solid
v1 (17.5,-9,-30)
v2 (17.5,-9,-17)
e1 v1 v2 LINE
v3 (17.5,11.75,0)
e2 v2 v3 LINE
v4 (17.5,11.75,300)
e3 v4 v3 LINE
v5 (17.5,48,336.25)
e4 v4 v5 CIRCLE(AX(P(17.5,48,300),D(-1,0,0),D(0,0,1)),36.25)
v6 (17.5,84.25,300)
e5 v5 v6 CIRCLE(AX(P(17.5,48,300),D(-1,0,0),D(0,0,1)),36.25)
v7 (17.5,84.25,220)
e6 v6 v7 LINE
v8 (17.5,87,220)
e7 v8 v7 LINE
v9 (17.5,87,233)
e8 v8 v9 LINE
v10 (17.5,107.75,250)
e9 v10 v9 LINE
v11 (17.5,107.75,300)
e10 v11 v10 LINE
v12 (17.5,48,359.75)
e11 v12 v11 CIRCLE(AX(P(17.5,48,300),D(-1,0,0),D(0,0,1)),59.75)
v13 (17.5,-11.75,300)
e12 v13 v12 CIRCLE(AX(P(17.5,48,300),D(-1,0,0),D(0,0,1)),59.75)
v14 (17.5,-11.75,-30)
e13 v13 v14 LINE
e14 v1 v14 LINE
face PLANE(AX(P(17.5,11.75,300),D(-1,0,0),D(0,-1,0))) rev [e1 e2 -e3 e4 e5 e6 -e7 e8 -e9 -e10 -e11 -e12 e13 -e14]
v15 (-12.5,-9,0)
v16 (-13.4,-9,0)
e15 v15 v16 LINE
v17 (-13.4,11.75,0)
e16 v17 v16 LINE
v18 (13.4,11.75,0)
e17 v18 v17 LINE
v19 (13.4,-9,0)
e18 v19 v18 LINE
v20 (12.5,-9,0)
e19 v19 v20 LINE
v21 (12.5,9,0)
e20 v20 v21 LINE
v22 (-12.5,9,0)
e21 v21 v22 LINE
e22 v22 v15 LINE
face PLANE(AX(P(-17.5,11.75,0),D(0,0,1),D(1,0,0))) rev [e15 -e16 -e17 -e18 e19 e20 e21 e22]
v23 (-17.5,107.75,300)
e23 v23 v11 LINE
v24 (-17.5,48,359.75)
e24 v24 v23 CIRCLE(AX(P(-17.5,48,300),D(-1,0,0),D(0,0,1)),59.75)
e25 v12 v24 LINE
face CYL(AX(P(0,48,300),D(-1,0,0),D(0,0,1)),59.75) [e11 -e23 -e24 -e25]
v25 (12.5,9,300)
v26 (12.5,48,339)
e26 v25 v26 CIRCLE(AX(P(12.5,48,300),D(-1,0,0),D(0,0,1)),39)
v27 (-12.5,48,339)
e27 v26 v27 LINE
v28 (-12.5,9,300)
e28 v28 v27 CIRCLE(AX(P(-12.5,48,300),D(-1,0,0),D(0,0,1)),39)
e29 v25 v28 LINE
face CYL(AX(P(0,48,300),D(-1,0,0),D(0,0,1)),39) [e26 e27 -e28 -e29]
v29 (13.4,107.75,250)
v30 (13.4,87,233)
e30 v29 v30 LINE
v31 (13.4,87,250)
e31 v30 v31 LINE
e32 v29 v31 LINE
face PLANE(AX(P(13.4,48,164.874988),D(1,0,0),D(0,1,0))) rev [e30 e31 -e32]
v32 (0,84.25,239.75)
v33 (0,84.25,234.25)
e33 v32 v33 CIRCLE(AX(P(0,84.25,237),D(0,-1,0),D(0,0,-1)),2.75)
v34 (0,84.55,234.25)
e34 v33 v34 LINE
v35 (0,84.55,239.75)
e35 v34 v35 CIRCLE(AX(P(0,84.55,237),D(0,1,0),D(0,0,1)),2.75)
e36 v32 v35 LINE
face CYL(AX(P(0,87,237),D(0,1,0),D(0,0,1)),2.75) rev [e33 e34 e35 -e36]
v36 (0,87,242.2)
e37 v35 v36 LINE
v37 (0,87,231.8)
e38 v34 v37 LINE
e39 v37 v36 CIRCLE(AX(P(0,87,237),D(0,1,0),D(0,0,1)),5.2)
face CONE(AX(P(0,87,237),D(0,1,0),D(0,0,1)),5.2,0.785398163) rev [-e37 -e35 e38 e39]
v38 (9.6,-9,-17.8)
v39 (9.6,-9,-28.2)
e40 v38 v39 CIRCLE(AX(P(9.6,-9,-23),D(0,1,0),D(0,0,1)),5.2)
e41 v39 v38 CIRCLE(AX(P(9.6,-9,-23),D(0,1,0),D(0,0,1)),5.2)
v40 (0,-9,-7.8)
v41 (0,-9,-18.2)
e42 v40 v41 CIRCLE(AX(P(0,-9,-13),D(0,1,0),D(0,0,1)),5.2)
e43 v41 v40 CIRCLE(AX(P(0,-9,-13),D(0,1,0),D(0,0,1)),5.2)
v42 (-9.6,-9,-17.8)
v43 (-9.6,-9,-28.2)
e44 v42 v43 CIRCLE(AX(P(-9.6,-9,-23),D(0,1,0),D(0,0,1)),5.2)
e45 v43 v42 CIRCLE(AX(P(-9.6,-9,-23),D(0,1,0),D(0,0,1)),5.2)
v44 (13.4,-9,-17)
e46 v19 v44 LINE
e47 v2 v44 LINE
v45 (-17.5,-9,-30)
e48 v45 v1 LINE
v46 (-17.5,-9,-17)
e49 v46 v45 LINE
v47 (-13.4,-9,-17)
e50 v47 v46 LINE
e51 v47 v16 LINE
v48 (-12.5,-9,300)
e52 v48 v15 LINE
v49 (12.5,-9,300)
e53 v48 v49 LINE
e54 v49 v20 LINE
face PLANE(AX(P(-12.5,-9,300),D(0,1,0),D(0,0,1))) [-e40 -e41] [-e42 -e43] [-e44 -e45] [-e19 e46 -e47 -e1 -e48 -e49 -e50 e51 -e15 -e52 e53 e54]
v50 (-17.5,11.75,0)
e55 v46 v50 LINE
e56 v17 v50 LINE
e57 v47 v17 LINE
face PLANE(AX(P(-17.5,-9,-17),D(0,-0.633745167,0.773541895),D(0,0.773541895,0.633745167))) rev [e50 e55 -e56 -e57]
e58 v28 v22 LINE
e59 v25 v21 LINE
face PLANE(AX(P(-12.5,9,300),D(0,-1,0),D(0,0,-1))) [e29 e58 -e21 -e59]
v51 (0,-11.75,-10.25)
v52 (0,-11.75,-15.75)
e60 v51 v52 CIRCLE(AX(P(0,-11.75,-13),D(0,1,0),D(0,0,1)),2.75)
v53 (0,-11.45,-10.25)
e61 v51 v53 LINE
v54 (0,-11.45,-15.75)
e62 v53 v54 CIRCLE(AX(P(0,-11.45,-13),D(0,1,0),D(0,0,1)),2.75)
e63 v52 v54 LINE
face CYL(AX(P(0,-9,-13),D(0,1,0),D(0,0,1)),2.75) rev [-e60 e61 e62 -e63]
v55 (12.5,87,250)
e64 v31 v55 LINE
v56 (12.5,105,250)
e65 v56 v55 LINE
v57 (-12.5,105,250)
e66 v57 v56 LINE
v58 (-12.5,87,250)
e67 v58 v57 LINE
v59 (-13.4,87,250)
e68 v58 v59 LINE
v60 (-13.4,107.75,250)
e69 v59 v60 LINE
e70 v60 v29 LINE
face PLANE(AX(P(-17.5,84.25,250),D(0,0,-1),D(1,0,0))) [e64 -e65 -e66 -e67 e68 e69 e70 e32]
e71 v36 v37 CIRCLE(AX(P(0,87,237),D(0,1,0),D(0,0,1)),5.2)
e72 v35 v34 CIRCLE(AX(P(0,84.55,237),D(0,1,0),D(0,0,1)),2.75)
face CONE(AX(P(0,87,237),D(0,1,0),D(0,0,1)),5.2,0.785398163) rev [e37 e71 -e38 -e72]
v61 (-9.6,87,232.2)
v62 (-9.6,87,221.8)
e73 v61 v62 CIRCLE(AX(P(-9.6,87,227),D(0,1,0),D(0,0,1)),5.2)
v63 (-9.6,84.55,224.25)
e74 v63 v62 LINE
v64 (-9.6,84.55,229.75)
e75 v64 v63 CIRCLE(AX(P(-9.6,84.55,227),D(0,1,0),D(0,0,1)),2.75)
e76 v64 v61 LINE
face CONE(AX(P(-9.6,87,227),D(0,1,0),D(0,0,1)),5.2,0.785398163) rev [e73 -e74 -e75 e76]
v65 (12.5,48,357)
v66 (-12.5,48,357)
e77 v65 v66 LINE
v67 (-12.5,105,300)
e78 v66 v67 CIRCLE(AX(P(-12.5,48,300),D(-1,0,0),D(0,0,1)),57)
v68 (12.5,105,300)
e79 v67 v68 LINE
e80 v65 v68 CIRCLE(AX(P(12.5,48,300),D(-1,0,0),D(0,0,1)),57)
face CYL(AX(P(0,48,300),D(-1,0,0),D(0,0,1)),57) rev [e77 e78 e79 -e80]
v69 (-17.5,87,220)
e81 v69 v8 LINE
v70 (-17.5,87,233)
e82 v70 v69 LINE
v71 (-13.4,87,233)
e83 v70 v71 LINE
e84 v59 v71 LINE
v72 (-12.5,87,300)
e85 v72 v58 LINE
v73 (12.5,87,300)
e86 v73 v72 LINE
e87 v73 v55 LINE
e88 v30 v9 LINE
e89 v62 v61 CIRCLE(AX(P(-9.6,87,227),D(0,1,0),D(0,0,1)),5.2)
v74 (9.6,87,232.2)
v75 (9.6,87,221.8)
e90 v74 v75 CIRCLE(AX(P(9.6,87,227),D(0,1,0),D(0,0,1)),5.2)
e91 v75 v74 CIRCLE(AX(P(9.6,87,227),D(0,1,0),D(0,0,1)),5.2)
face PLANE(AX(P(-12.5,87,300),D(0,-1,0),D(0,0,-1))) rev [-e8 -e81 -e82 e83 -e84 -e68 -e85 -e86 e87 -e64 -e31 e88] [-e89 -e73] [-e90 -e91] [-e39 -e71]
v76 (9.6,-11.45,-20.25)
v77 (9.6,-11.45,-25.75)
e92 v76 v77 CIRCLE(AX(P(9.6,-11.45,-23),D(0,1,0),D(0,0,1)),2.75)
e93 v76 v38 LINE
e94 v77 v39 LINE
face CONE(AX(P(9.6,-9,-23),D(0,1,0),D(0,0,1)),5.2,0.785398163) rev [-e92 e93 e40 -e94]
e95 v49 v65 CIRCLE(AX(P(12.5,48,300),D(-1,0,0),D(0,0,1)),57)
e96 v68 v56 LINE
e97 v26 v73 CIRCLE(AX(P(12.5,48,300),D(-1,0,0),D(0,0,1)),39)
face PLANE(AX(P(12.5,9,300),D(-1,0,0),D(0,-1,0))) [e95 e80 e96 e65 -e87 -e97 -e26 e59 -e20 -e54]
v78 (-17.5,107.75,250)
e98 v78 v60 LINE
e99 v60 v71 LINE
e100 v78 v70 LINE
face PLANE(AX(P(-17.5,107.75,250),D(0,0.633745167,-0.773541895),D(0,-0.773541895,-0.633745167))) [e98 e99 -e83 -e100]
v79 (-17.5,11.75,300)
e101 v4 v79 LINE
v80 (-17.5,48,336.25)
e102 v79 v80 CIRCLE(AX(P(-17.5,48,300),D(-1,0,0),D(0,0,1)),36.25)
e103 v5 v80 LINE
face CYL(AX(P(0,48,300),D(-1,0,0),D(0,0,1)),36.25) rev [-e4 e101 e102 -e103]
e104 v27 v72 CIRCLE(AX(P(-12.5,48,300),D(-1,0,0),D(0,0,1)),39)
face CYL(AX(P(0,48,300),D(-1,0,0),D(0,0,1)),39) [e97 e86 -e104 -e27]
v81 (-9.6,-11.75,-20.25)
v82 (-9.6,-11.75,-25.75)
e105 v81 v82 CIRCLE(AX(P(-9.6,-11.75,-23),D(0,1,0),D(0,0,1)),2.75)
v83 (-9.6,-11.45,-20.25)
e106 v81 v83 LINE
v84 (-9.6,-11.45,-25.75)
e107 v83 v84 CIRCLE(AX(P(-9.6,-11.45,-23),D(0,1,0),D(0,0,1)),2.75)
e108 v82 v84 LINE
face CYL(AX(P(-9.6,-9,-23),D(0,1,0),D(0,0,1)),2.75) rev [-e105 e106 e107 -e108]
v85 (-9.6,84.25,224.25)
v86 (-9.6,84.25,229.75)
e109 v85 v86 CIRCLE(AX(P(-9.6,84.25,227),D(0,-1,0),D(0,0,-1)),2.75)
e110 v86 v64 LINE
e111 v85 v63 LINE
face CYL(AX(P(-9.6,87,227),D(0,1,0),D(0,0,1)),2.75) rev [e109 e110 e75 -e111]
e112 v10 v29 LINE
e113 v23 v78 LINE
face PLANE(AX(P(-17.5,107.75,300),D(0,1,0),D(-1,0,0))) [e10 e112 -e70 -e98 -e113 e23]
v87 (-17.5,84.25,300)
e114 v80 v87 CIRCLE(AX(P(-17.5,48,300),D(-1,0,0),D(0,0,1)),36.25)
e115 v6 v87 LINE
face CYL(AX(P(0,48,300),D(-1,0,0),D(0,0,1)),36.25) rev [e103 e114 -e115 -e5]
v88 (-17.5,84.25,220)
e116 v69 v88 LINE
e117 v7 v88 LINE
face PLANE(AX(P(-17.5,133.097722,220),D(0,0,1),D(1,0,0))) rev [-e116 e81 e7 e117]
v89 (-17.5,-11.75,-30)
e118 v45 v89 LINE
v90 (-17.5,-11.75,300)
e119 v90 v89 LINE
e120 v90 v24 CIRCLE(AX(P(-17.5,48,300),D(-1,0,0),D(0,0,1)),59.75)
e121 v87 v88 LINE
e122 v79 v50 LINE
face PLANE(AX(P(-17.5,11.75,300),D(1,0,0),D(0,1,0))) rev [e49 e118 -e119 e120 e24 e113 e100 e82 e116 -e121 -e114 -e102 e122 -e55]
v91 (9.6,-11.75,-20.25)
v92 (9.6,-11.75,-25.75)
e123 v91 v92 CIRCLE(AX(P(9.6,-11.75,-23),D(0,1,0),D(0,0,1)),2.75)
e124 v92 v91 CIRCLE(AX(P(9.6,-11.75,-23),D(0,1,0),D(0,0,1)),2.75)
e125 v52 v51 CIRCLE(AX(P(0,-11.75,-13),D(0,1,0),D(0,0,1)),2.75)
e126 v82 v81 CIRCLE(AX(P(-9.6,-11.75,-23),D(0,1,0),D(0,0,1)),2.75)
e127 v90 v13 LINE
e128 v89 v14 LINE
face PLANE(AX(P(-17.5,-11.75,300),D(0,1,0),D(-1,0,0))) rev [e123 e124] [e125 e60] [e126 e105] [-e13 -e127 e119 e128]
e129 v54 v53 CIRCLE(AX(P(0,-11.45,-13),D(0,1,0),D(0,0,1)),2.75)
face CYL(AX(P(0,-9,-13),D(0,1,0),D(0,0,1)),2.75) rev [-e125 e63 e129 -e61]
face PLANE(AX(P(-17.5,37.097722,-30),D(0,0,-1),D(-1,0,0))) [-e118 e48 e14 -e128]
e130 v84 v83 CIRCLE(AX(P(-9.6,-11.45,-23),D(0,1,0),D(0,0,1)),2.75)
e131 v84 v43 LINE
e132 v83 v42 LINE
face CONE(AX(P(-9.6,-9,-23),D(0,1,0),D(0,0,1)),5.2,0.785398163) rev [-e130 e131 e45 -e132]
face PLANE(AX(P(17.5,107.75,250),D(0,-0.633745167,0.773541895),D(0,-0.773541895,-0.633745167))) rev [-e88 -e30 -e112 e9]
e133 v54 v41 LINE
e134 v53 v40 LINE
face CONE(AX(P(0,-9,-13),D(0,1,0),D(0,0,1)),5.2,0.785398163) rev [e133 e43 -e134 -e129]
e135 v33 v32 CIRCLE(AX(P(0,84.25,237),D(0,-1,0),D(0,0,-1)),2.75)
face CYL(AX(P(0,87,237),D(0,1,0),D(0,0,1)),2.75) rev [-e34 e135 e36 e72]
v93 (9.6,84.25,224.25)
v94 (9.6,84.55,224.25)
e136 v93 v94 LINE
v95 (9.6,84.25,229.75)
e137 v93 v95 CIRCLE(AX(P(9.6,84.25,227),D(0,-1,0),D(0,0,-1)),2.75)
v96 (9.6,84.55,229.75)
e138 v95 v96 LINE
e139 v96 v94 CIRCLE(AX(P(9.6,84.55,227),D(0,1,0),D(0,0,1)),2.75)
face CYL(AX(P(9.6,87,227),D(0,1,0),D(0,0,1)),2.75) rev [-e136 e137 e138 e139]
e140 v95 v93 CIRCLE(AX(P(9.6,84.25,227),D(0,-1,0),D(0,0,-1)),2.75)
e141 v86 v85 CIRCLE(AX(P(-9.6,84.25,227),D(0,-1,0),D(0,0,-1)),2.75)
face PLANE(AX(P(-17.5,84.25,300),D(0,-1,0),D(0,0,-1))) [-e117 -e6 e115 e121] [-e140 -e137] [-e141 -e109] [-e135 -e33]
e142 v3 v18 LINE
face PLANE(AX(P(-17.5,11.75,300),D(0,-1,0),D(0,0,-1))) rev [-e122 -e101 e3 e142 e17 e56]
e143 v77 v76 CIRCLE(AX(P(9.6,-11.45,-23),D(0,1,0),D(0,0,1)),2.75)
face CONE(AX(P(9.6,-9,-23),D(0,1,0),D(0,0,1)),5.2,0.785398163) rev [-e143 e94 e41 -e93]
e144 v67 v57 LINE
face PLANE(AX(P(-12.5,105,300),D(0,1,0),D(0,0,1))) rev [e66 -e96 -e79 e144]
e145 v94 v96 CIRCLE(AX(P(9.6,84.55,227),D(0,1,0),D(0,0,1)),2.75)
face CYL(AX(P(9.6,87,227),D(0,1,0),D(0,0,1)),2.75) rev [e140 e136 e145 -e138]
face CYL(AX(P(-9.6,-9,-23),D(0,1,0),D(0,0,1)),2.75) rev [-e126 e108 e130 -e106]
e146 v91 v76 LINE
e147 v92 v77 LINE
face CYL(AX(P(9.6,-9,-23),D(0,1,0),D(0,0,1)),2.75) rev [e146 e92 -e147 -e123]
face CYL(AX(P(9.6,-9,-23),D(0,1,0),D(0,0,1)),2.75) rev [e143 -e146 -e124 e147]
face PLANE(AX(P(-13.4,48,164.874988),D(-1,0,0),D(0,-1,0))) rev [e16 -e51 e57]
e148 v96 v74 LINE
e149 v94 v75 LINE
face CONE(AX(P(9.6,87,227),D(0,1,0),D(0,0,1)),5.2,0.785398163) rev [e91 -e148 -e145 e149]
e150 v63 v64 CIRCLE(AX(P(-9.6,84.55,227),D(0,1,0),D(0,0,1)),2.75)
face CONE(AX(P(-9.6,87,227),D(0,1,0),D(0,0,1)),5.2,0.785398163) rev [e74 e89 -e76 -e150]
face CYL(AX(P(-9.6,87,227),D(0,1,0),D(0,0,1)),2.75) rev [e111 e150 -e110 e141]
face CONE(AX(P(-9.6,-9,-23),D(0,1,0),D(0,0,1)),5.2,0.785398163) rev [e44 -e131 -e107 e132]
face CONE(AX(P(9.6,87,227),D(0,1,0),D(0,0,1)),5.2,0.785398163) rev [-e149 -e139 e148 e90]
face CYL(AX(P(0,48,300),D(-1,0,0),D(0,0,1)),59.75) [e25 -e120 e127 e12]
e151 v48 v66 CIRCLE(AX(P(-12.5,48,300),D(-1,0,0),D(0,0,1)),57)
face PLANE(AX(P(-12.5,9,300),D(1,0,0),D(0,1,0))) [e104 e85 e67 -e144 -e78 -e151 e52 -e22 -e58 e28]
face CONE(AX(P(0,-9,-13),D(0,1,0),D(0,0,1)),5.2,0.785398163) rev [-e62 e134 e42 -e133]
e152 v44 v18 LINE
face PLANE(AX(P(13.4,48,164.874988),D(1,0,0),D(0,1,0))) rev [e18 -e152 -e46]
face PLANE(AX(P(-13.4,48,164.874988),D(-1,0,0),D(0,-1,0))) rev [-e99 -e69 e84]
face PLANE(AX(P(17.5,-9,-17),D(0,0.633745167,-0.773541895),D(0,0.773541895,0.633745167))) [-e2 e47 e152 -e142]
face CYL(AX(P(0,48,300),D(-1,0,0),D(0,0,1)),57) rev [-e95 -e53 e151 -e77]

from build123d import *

# Parameters (mm, degrees)
SECTION_SIZE_W                              = 35
SECTION_SIZE_H                              = 23.5
SECTION_SIZE_W_2                            = 25
SECTION_SIZE_H_2                            = 18
SKETCH2_W                                   = 35
SKETCH2_H                                   = 30
FITTING114_4_12PZ_1_DEPTH                   = 2.75
SKETCH6_W                                   = 35
SKETCH6_H                                   = 30
FITTING114_4_12PZ_2_DEPTH                   = 2.75
RIB_E_REACH                                 = 379.167
SKETCH9_WALL_W                              = 783.159137046
SKETCH9_WALL_H                              = 4.1
RIB_Z_REACH                                 = 379.167
SKETCH10_WALL_W                             = 783.159137046
SKETCH10_WALL_H                             = 4.1
M5_FLAT_HEAD_SCREW_COUNTERSINK1_AT_2_COUNT  = 2
M5_FLAT_HEAD_SCREW_COUNTERSINK1_AT_2_PITCH  = 13.862178761
M5_FLAT_HEAD_SCREW_COUNTERSINK1_AT_3_COUNT  = 2
M5_FLAT_HEAD_SCREW_COUNTERSINK1_AT_3_PITCH  = 19.2
M5_FLAT_HEAD_SCREW_COUNTERSINK2_D           = 5.5
M5_FLAT_HEAD_SCREW_COUNTERSINK2_DEPTH       = 35
M5_FLAT_HEAD_SCREW_COUNTERSINK2_CSINK_D     = 10.4
M5_FLAT_HEAD_SCREW_COUNTERSINK2_CSINK_ANGLE = 90
M5_FLAT_HEAD_SCREW_COUNTERSINK2_TIP         = 1.652366702


with BuildPart() as part:
    # Chain: sweep along a path in Length Path
    with BuildLine(Plane(origin=(0, 0, 0), x_dir=(0, 0, -1), z_dir=(1, 0, 0))) as chain_path:
        Line((-250, 96), (-300, 96))
        ThreePointArc((-300, 96), (-348, 48), (-300, 0))
        Line((-300, 0), (0, 0))
    # Section Size → Chain (sweep)
    with BuildSketch(Plane.XY):
        Rectangle(SECTION_SIZE_W, SECTION_SIZE_H)
        Rectangle(SECTION_SIZE_W_2, SECTION_SIZE_H_2, mode=Mode.SUBTRACT)
    sweep(path=chain_path.line)

    # Sketch2 → Fitting114.4.12PZ-1 (add)
    with BuildSketch(Plane(origin=(0, 84.25, 0), x_dir=(1, 0, 0), z_dir=(0, 1, 0))):
        with Locations((0, -235)):
            Rectangle(SKETCH2_W, SKETCH2_H)
    extrude(amount=FITTING114_4_12PZ_1_DEPTH)

    # Sketch6 → Fitting114.4.12PZ-2 (add)
    with BuildSketch(Plane.XZ.offset(11.75)):
        with Locations((0, -15)):
            Rectangle(SKETCH6_W, SKETCH6_H)
    extrude(amount=-FITTING114_4_12PZ_2_DEPTH)

    # Sketch9 wall → E (add, up to next)
    with BuildSketch(Plane(origin=(17.5, 97.375, 241.5), x_dir=(0, -0.773541895, -0.633745166988), z_dir=(0, 0.633745166988, -0.773541895)), mode=Mode.PRIVATE) as rib_e_sk1:
        with Locations((0, 2.05)):
            Rectangle(SKETCH9_WALL_W, SKETCH9_WALL_H)
    rib_e_tool1 = extrude(rib_e_sk1.sketch, amount=-RIB_E_REACH, mode=Mode.PRIVATE) - part.part
    rib_e = rib_e_tool1.solids().sort_by_distance((17.5, 97.375, 241.5))[0]
    add(rib_e)

    # Sketch10 wall → Z (add, up to next)
    with BuildSketch(Plane(origin=(17.5, 1.375, -8.5), x_dir=(0, 0.773541895, 0.633745166988), z_dir=(0, -0.633745166988, 0.773541895)), mode=Mode.PRIVATE) as rib_z_sk1:
        with Locations((0, 2.05)):
            Rectangle(SKETCH10_WALL_W, SKETCH10_WALL_H)
    rib_z_tool1 = extrude(rib_z_sk1.sketch, amount=RIB_Z_REACH, mode=Mode.PRIVATE) - part.part
    rib_z = rib_z_tool1.solids().sort_by_distance((17.5, 1.375, -8.5))[0]
    add(rib_z)

    # Drag: E, Z across plane
    add(rib_e.mirror(Plane(origin=(0, 0, 0), x_dir=(0, 0, 1), z_dir=(1, 0, 0))))
    add(rib_z.mirror(Plane(origin=(0, 0, 0), x_dir=(0, 0, 1), z_dir=(1, 0, 0))))

    # Sketch17 → M5 Flat Head Screw Countersink1 (revolve, cut)
    with BuildSketch(Plane(origin=(-9.6, -9, -23), x_dir=(0, 0, 1), z_dir=(1, 0, 0))):
        Polygon((0, 0), (0, 2.75), (2.75, 2.75), (2.75, 2.45), (5.2, 0), align=None)
    m5_flat_head_screw_countersink1 = revolve(axis=Axis((-9.6, -2.65, -23), (0, -1, 0)), mode=Mode.SUBTRACT)

    # M5 Flat Head Screw Countersink1 at 2: M5 Flat Head Screw Countersink1 ×2
    with Locations(*[Vector(0.6925318281897137, 0, 0.7213873210309515) * (i * M5_FLAT_HEAD_SCREW_COUNTERSINK1_AT_2_PITCH) for i in range(1, M5_FLAT_HEAD_SCREW_COUNTERSINK1_AT_2_COUNT)]):
        add(m5_flat_head_screw_countersink1, mode=Mode.SUBTRACT)

    # M5 Flat Head Screw Countersink1 at 3: M5 Flat Head Screw Countersink1 ×2
    with Locations(*[(i * M5_FLAT_HEAD_SCREW_COUNTERSINK1_AT_3_PITCH, 0, 0) for i in range(1, M5_FLAT_HEAD_SCREW_COUNTERSINK1_AT_3_COUNT)]):
        add(m5_flat_head_screw_countersink1, mode=Mode.SUBTRACT)

    # M5 Flat Head Screw Countersink2
    with Locations(Plane(origin=(-9.6, 87, 227), x_dir=(0, 0, 1), z_dir=(0, 1, 0))):
        with Locations((0, 0), (10, 9.6), (0, 19.2)):
            CounterSinkHole(M5_FLAT_HEAD_SCREW_COUNTERSINK2_D / 2, M5_FLAT_HEAD_SCREW_COUNTERSINK2_CSINK_D / 2, depth=M5_FLAT_HEAD_SCREW_COUNTERSINK2_DEPTH, counter_sink_angle=M5_FLAT_HEAD_SCREW_COUNTERSINK2_CSINK_ANGLE)
            with Locations((0, 0, -(M5_FLAT_HEAD_SCREW_COUNTERSINK2_DEPTH + M5_FLAT_HEAD_SCREW_COUNTERSINK2_TIP / 2))):  # 118° drill point
                Cone(0, M5_FLAT_HEAD_SCREW_COUNTERSINK2_D / 2, M5_FLAT_HEAD_SCREW_COUNTERSINK2_TIP, mode=Mode.SUBTRACT)


solid = part.part
